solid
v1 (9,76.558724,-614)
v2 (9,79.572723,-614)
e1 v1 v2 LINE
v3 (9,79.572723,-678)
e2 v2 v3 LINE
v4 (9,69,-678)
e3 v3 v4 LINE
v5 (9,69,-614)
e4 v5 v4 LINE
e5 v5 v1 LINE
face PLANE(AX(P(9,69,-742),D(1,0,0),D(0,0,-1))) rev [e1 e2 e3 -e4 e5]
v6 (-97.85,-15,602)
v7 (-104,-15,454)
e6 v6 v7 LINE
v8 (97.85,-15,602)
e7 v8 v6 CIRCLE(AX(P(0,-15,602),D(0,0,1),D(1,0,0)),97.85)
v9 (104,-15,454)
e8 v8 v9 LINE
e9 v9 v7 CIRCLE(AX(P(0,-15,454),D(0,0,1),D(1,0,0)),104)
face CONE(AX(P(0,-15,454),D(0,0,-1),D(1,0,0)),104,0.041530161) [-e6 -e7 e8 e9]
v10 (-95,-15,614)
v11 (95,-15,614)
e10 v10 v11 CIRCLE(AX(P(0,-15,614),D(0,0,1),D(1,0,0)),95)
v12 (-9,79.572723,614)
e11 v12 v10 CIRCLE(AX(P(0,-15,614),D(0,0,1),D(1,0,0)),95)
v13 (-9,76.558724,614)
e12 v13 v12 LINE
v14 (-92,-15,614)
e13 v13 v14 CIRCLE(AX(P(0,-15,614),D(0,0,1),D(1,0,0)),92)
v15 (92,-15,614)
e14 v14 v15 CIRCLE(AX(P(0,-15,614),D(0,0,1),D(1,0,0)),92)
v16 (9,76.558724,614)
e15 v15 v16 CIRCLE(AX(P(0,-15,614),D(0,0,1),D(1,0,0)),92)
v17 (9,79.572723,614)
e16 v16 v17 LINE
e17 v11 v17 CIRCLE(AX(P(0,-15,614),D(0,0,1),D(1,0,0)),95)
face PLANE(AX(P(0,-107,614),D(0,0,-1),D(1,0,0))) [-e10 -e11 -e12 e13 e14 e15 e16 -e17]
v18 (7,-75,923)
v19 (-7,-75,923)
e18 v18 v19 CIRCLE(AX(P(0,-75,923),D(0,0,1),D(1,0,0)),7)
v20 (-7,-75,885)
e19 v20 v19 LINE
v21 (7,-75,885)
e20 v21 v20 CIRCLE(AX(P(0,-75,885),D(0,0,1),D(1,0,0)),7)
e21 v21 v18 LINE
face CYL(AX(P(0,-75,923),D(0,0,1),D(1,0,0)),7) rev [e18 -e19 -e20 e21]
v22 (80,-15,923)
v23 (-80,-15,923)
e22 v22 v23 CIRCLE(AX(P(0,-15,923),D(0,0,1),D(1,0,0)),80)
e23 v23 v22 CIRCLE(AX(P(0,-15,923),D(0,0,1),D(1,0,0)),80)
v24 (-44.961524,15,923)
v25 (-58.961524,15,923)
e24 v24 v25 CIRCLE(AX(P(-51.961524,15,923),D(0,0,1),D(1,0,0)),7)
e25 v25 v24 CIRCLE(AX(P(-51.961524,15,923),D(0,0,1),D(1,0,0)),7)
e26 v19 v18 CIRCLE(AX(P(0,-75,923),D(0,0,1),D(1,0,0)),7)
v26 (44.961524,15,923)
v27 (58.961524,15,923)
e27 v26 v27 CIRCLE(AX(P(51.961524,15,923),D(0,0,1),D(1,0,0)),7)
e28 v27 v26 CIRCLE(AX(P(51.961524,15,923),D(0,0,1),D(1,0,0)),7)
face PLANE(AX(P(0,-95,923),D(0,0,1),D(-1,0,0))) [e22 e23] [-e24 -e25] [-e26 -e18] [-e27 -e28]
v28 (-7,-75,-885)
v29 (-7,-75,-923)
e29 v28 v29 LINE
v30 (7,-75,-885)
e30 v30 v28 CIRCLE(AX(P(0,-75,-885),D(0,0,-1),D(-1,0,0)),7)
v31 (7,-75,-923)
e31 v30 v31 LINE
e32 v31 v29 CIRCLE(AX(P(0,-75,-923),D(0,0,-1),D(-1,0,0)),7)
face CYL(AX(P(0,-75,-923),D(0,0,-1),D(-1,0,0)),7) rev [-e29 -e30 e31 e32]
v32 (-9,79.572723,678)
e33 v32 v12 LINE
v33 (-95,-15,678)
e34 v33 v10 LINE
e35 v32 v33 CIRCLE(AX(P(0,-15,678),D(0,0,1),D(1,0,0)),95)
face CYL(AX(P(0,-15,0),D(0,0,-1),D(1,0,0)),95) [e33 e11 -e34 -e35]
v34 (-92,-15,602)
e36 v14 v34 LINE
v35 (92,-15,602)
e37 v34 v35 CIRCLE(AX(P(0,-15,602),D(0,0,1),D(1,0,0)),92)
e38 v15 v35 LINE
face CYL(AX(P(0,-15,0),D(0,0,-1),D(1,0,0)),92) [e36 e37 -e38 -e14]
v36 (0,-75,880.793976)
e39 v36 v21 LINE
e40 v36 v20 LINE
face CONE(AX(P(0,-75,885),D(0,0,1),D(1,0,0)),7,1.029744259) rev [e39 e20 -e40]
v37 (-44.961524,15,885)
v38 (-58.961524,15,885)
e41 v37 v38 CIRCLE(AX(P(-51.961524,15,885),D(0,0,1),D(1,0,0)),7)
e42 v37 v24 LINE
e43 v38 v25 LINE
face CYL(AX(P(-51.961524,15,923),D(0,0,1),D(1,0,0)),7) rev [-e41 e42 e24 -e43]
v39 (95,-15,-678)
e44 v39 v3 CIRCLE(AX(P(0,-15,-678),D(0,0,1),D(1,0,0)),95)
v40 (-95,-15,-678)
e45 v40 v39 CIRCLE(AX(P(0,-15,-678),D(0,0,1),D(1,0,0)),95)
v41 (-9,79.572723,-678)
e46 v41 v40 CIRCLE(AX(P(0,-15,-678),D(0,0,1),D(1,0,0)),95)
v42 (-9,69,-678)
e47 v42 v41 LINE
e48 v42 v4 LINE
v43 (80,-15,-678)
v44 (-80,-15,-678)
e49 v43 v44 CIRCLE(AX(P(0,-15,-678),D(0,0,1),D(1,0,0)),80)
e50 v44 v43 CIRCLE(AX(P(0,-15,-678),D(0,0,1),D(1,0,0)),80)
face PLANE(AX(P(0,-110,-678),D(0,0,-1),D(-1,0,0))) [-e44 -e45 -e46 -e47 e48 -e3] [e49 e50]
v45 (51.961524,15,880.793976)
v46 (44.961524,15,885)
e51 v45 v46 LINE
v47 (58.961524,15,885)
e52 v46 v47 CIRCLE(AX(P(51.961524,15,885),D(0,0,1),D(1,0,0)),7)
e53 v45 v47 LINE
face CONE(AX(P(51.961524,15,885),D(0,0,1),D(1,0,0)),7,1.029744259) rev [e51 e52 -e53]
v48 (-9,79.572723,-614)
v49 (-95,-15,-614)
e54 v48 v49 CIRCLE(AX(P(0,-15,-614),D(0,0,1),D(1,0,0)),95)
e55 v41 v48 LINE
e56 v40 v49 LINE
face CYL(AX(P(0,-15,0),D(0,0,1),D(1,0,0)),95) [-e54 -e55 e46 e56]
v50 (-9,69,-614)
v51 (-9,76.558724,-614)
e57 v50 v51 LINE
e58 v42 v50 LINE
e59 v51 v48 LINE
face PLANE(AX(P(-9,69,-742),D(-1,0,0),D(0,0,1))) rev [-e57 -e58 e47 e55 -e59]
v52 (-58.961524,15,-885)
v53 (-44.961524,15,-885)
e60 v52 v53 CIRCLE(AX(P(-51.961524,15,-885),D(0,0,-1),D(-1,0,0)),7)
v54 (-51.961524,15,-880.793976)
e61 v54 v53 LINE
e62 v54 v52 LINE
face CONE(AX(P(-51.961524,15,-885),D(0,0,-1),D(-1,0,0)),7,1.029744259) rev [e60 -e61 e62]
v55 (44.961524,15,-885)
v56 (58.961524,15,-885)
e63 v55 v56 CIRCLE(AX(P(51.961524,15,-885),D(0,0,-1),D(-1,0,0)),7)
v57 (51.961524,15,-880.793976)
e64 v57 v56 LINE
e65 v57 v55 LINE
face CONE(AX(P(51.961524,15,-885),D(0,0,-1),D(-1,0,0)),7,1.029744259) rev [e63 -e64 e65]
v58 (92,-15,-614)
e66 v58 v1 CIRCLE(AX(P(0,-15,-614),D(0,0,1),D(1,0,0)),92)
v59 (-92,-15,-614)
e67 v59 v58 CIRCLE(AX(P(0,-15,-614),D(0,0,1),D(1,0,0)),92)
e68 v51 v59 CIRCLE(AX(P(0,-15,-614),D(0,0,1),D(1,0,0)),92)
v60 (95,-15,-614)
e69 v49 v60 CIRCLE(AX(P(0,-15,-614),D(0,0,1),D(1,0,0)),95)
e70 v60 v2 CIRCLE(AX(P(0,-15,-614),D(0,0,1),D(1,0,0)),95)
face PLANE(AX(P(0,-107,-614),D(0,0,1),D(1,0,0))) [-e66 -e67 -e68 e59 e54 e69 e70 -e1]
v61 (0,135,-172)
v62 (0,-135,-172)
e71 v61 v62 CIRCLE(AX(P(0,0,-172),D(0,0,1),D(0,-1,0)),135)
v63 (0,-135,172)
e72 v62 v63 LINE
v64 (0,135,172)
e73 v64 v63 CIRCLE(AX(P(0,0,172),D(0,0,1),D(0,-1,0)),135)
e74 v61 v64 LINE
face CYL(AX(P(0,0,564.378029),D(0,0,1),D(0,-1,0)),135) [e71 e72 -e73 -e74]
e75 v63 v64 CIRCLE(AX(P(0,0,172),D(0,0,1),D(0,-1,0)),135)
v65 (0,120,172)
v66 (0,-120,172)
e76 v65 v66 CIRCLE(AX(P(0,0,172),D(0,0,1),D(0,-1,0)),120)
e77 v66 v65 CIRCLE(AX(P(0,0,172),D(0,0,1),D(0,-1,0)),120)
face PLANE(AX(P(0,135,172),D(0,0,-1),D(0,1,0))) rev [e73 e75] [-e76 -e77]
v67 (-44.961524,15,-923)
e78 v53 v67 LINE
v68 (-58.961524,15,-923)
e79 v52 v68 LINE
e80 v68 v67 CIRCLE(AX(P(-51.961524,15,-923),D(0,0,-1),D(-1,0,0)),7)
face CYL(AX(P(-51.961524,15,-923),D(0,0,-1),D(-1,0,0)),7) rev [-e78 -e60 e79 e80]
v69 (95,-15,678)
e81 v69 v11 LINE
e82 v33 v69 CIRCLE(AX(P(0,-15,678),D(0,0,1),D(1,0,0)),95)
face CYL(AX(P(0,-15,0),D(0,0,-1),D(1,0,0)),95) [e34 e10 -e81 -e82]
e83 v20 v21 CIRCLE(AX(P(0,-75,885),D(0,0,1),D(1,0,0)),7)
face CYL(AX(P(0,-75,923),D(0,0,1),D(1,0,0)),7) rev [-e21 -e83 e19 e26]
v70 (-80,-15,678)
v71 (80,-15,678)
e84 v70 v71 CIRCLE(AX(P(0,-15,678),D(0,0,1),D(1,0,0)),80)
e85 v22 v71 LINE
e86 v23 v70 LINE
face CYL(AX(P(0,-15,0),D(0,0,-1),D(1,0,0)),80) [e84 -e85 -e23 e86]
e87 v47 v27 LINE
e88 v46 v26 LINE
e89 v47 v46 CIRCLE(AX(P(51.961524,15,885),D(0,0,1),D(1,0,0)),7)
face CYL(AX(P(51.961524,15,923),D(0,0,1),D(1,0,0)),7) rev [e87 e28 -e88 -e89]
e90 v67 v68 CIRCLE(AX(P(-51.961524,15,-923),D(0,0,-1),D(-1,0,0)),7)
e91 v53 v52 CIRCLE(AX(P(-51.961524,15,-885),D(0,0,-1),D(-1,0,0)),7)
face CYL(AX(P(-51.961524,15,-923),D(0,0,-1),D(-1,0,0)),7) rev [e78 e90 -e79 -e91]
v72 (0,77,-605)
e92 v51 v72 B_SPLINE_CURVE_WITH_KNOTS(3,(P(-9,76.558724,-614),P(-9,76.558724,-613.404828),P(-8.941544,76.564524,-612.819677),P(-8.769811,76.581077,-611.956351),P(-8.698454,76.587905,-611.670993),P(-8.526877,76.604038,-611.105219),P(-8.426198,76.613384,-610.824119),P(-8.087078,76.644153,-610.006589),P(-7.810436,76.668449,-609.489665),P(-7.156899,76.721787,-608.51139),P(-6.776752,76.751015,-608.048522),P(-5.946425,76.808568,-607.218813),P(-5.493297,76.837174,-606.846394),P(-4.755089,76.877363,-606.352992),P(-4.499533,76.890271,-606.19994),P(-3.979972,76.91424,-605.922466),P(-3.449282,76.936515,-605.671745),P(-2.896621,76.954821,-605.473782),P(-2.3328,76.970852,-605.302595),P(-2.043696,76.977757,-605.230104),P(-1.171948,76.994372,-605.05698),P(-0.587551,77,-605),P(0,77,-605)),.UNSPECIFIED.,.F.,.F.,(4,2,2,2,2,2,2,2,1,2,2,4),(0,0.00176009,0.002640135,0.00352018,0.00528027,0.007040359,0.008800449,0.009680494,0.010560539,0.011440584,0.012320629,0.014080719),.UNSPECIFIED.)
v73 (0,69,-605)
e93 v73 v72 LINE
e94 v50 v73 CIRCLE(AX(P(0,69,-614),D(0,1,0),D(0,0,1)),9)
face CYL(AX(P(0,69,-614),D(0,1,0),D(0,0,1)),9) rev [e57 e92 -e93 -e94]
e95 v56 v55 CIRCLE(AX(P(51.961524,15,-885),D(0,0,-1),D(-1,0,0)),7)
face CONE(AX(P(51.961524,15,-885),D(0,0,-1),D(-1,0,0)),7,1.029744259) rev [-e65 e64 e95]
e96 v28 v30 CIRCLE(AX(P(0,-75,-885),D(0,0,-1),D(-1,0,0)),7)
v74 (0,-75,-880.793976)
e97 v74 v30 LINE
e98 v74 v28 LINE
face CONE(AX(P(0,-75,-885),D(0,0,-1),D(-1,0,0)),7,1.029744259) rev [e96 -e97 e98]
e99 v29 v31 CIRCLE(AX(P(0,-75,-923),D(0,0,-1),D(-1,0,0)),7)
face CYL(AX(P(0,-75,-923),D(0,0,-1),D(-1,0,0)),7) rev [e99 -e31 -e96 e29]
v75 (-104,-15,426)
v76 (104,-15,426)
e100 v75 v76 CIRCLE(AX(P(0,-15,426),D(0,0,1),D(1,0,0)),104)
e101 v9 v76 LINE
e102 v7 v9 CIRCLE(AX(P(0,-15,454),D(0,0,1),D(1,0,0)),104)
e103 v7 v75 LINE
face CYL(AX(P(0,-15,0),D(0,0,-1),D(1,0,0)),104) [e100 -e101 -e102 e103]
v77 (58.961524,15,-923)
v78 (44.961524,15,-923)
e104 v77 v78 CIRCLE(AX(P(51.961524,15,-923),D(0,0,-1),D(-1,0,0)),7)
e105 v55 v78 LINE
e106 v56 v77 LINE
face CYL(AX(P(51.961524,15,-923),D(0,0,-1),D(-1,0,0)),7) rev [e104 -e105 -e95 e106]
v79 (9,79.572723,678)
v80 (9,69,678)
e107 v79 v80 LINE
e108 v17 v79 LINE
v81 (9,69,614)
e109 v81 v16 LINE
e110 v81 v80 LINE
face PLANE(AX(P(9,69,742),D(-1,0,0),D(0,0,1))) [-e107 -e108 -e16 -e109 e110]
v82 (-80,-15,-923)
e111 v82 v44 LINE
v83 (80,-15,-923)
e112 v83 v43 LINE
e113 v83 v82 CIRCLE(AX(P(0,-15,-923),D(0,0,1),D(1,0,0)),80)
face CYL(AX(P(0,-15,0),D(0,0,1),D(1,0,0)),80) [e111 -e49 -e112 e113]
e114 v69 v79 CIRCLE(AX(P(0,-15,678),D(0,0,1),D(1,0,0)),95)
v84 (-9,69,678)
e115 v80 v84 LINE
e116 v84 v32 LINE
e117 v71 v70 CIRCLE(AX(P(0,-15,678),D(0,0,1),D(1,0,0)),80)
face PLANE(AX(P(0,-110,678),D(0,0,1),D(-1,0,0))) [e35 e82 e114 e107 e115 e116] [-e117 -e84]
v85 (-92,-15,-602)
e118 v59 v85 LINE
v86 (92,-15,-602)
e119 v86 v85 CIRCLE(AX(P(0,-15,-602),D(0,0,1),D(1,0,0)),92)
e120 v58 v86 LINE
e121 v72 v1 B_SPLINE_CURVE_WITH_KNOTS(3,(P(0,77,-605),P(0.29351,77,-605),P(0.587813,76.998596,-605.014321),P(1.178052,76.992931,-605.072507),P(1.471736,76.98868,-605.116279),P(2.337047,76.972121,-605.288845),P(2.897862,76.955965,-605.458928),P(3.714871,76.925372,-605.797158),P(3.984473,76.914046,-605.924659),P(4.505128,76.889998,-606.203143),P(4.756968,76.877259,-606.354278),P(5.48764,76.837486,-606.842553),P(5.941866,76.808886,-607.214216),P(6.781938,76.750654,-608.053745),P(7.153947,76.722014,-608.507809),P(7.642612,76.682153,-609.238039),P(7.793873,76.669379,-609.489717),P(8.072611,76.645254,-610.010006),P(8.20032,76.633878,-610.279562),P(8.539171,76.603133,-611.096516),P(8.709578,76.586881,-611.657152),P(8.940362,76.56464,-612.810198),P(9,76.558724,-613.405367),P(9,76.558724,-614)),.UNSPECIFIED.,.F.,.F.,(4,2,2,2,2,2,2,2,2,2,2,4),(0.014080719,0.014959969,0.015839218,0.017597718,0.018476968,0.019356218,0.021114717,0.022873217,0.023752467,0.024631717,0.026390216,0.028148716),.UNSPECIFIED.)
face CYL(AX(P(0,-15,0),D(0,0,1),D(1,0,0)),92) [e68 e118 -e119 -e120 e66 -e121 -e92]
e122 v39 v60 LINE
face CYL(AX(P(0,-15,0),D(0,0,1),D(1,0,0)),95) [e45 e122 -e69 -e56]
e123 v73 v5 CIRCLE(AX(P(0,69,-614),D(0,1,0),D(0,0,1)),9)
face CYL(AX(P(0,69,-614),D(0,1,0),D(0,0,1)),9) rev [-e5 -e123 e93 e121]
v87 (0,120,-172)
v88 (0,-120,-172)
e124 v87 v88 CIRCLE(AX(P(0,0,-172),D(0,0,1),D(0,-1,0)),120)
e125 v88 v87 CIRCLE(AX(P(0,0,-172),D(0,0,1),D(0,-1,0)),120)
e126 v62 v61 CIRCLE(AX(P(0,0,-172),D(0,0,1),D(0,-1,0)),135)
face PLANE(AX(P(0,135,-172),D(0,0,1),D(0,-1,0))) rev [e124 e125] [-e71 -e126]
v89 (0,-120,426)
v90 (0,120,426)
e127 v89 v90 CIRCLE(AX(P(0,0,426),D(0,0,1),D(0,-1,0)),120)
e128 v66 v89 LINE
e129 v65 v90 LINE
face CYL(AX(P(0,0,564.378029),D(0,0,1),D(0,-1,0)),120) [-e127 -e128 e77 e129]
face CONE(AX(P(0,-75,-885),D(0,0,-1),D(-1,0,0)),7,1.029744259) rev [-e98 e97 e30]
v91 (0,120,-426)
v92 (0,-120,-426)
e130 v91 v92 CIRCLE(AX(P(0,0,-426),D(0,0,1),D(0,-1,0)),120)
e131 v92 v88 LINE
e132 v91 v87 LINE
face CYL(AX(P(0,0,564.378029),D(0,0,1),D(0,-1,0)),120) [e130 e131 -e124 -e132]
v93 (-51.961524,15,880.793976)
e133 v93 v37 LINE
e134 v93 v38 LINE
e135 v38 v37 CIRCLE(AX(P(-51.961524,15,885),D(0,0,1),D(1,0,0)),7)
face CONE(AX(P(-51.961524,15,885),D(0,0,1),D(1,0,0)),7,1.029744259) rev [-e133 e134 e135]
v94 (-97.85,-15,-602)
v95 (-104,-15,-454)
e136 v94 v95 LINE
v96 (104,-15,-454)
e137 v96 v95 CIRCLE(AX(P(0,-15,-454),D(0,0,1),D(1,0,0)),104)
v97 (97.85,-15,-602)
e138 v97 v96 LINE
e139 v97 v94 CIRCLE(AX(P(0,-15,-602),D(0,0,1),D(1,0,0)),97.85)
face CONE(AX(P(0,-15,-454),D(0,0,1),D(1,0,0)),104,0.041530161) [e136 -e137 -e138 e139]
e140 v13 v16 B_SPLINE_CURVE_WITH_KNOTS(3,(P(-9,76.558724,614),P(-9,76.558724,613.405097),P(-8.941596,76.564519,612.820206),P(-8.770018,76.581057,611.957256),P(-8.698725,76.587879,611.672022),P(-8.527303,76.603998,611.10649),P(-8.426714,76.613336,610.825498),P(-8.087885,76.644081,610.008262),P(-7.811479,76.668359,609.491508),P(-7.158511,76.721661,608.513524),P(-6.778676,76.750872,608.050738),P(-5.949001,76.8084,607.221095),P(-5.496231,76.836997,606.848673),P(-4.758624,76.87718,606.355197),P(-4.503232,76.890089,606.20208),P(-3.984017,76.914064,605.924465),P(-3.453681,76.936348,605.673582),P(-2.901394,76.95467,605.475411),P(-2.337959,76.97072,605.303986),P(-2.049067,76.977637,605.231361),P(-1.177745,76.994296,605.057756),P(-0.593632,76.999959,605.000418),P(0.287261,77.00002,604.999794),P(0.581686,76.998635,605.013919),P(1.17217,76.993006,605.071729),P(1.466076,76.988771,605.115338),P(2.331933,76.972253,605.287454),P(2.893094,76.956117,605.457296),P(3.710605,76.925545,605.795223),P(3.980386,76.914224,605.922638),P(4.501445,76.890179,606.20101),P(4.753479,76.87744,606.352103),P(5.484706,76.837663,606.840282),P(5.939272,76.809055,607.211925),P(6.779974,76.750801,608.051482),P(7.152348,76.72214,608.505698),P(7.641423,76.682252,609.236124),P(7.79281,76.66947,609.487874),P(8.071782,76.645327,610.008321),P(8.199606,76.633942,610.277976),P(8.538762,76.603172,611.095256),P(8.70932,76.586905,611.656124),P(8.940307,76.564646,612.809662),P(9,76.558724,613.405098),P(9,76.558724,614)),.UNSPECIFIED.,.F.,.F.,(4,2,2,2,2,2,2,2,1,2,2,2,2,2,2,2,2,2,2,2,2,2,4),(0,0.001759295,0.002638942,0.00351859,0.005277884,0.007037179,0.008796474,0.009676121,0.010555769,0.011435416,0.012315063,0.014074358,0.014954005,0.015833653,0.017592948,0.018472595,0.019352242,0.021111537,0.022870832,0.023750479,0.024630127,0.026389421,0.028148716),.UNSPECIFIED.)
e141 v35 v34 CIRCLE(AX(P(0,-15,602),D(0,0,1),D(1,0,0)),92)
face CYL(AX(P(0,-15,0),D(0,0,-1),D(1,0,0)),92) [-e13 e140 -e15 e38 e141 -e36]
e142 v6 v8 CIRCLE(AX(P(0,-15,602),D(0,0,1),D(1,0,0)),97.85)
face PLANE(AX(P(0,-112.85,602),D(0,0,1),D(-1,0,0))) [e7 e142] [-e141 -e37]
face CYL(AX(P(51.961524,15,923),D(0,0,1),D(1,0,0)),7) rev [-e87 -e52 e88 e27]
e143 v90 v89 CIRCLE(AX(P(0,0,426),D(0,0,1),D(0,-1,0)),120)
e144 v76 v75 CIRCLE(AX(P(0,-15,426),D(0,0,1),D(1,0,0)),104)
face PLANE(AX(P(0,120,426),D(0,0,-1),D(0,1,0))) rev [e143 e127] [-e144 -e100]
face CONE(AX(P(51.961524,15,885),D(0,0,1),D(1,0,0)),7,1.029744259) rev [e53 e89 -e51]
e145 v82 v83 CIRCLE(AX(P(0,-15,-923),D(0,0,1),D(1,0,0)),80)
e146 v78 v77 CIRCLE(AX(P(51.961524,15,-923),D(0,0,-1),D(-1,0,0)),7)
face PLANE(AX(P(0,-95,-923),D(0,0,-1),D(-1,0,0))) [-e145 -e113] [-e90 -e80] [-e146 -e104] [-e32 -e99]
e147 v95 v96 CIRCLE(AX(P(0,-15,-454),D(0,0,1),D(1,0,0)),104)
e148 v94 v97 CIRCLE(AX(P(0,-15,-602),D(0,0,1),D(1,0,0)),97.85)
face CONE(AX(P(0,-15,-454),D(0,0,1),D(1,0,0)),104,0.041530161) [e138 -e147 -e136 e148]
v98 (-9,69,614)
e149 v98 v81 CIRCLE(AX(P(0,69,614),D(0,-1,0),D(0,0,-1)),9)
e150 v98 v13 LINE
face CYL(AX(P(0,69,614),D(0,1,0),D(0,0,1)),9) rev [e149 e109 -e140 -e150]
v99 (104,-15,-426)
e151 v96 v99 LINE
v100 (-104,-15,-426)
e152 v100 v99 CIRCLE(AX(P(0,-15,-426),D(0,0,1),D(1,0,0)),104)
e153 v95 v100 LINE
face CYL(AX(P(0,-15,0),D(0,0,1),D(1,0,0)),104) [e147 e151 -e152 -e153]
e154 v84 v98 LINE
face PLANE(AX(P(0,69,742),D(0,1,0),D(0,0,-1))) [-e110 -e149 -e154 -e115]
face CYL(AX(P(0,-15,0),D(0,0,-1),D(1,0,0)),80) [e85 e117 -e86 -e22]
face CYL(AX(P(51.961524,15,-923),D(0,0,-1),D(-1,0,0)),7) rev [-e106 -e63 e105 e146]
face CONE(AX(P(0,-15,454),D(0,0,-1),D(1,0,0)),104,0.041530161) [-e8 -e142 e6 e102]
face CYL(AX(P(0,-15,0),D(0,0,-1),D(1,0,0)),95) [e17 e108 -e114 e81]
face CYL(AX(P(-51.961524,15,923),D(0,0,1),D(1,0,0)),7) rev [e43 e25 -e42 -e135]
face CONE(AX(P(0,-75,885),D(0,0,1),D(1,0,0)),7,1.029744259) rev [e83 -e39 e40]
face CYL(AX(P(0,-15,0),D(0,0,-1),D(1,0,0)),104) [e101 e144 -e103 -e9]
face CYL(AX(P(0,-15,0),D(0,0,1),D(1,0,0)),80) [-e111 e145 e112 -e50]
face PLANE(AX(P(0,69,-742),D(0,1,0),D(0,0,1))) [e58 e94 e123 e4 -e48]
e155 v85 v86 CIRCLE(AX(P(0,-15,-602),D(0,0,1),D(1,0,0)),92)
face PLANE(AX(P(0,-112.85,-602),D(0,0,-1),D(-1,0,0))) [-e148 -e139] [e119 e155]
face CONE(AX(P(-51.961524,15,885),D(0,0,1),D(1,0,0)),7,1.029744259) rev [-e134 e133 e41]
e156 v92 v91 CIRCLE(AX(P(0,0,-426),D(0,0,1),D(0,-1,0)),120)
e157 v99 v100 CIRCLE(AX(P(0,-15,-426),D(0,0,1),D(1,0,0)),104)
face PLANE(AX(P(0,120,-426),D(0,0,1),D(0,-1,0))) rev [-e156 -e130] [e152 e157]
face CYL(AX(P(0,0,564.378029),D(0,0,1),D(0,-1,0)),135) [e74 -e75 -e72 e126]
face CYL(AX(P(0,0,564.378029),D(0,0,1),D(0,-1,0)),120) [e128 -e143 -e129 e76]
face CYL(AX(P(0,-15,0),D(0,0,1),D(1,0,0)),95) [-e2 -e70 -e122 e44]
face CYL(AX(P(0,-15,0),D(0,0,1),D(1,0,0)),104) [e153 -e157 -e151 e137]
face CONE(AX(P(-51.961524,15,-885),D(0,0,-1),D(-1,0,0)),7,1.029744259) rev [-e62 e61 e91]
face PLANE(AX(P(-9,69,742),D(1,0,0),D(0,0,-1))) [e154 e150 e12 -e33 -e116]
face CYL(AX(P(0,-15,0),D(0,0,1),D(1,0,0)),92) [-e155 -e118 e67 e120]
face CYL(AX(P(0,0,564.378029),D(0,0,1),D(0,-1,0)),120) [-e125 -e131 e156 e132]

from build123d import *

# Parameters (mm, degrees)
CUT_EXTRUDE3_START = 95.1
CUT_EXTRUDE3_DEPTH = 26.1
CIRPATTERN1_COUNT  = 3


with BuildPart() as part:
    # Sketch2 → Revolve1 (revolve)
    with BuildSketch(Plane(origin=(0, 0, 0), x_dir=(0, 0, -1), z_dir=(1, 0, 0)), mode=Mode.PRIVATE) as revolve1_sk:
        Polygon((-172, 135), (172, 135), (172, 120), (426, 120), (426, 0), (0, 0), (-426, 0), (-426, 120), (-172, 120), align=None)
    revolve(revolve1_sk.sketch.rotate(Axis((0, 0, 564.378028921), (0, 0, -1)), 180), axis=Axis((0, 0, 564.378028921), (0, 0, -1)))

    # Sketch3 → Revolve2 (revolve)
    with BuildSketch(Plane(origin=(0, 0, 0), x_dir=(0, 0, -1), z_dir=(1, 0, 0)), mode=Mode.PRIVATE) as revolve2_sk:
        Polygon((426, -119), (426, -15), (923, -15), (923, -95), (678, -95), (678, -110), (614, -110), (614, -107), (602, -107), (602, -112.85), (454, -119), align=None)
    revolve2 = revolve(revolve2_sk.sketch.rotate(Axis((0, -15, 0), (0, 0, -1)), 270), axis=Axis((0, -15, 0), (0, 0, -1)))

    # Mirror1: Revolve2 across plane
    add(revolve2.mirror(Plane.XY))

    # Sketch5 → Cut-Extrude3 (cut)
    with BuildSketch(Plane(origin=(0, 0, 0), x_dir=(1, 0, 0), z_dir=(0, 1, 0)).offset(CUT_EXTRUDE3_START)):
        with BuildLine():
            Line((9, 742), (9, 614))
            ThreePointArc((9, 614), (0, 605), (-9, 614))
            Line((-9, 614), (-9, 742))
            ThreePointArc((-9, 742), (0, 751), (9, 742))
        make_face()
    cut_extrude3 = extrude(amount=-CUT_EXTRUDE3_DEPTH, mode=Mode.SUBTRACT)

    # Mirror2: Cut-Extrude3 across plane
    add(cut_extrude3.mirror(Plane.XY), mode=Mode.SUBTRACT)

    # Sketch7 → M16 Tapped Hole1 (revolve, cut)
    with BuildSketch(Plane(origin=(-51.961524227, 15, -923), x_dir=(0, 1, 0), z_dir=(1, 0, 0))):
        Polygon((0, 0), (0, 42.206024333), (7, 38), (7, 0), align=None)
    m16_tapped_hole1 = revolve(axis=Axis((-51.961524227, 15, -929.35), (0, 0, 1)), mode=Mode.SUBTRACT)

    # CirPattern1: M16 Tapped Hole1 ×3 about axis
    cirpattern1_axis = Axis((0, -15, 0), (0, 0, 1))
    for i in range(1, CIRPATTERN1_COUNT):
        add(m16_tapped_hole1.rotate(cirpattern1_axis, i * 360 / CIRPATTERN1_COUNT), mode=Mode.SUBTRACT)

    # Mirror3: M16 Tapped Hole1 across plane
    add(m16_tapped_hole1.mirror(Plane.XY), mode=Mode.SUBTRACT)

    # Mirror3 copy 1 sketch → Mirror3 copy 1 (revolve, cut)
    with BuildSketch(Plane(origin=(0, -75, 923), x_dir=(-0.8660254037844387, -0.4999999999999998, 0), z_dir=(-0.4999999999999998, 0.8660254037844387, 0))):
        Polygon((0, 0), (0, -42.206024333), (7, -38), (7, 0), align=None)
    revolve(axis=Axis((0, -75, 929.35), (0, 0, 1)), mode=Mode.SUBTRACT)

    # Mirror3 copy 2 sketch → Mirror3 copy 2 (revolve, cut)
    with BuildSketch(Plane(origin=(51.961524227, 15, 923), x_dir=(0.8660254037844384, -0.5000000000000004, 0), z_dir=(-0.5000000000000004, -0.8660254037844384, 0))):
        Polygon((0, 0), (0, -42.206024333), (7, -38), (7, 0), align=None)
    revolve(axis=Axis((51.961524227, 15, 929.35), (0, 0, 1)), mode=Mode.SUBTRACT)


solid = part.part
